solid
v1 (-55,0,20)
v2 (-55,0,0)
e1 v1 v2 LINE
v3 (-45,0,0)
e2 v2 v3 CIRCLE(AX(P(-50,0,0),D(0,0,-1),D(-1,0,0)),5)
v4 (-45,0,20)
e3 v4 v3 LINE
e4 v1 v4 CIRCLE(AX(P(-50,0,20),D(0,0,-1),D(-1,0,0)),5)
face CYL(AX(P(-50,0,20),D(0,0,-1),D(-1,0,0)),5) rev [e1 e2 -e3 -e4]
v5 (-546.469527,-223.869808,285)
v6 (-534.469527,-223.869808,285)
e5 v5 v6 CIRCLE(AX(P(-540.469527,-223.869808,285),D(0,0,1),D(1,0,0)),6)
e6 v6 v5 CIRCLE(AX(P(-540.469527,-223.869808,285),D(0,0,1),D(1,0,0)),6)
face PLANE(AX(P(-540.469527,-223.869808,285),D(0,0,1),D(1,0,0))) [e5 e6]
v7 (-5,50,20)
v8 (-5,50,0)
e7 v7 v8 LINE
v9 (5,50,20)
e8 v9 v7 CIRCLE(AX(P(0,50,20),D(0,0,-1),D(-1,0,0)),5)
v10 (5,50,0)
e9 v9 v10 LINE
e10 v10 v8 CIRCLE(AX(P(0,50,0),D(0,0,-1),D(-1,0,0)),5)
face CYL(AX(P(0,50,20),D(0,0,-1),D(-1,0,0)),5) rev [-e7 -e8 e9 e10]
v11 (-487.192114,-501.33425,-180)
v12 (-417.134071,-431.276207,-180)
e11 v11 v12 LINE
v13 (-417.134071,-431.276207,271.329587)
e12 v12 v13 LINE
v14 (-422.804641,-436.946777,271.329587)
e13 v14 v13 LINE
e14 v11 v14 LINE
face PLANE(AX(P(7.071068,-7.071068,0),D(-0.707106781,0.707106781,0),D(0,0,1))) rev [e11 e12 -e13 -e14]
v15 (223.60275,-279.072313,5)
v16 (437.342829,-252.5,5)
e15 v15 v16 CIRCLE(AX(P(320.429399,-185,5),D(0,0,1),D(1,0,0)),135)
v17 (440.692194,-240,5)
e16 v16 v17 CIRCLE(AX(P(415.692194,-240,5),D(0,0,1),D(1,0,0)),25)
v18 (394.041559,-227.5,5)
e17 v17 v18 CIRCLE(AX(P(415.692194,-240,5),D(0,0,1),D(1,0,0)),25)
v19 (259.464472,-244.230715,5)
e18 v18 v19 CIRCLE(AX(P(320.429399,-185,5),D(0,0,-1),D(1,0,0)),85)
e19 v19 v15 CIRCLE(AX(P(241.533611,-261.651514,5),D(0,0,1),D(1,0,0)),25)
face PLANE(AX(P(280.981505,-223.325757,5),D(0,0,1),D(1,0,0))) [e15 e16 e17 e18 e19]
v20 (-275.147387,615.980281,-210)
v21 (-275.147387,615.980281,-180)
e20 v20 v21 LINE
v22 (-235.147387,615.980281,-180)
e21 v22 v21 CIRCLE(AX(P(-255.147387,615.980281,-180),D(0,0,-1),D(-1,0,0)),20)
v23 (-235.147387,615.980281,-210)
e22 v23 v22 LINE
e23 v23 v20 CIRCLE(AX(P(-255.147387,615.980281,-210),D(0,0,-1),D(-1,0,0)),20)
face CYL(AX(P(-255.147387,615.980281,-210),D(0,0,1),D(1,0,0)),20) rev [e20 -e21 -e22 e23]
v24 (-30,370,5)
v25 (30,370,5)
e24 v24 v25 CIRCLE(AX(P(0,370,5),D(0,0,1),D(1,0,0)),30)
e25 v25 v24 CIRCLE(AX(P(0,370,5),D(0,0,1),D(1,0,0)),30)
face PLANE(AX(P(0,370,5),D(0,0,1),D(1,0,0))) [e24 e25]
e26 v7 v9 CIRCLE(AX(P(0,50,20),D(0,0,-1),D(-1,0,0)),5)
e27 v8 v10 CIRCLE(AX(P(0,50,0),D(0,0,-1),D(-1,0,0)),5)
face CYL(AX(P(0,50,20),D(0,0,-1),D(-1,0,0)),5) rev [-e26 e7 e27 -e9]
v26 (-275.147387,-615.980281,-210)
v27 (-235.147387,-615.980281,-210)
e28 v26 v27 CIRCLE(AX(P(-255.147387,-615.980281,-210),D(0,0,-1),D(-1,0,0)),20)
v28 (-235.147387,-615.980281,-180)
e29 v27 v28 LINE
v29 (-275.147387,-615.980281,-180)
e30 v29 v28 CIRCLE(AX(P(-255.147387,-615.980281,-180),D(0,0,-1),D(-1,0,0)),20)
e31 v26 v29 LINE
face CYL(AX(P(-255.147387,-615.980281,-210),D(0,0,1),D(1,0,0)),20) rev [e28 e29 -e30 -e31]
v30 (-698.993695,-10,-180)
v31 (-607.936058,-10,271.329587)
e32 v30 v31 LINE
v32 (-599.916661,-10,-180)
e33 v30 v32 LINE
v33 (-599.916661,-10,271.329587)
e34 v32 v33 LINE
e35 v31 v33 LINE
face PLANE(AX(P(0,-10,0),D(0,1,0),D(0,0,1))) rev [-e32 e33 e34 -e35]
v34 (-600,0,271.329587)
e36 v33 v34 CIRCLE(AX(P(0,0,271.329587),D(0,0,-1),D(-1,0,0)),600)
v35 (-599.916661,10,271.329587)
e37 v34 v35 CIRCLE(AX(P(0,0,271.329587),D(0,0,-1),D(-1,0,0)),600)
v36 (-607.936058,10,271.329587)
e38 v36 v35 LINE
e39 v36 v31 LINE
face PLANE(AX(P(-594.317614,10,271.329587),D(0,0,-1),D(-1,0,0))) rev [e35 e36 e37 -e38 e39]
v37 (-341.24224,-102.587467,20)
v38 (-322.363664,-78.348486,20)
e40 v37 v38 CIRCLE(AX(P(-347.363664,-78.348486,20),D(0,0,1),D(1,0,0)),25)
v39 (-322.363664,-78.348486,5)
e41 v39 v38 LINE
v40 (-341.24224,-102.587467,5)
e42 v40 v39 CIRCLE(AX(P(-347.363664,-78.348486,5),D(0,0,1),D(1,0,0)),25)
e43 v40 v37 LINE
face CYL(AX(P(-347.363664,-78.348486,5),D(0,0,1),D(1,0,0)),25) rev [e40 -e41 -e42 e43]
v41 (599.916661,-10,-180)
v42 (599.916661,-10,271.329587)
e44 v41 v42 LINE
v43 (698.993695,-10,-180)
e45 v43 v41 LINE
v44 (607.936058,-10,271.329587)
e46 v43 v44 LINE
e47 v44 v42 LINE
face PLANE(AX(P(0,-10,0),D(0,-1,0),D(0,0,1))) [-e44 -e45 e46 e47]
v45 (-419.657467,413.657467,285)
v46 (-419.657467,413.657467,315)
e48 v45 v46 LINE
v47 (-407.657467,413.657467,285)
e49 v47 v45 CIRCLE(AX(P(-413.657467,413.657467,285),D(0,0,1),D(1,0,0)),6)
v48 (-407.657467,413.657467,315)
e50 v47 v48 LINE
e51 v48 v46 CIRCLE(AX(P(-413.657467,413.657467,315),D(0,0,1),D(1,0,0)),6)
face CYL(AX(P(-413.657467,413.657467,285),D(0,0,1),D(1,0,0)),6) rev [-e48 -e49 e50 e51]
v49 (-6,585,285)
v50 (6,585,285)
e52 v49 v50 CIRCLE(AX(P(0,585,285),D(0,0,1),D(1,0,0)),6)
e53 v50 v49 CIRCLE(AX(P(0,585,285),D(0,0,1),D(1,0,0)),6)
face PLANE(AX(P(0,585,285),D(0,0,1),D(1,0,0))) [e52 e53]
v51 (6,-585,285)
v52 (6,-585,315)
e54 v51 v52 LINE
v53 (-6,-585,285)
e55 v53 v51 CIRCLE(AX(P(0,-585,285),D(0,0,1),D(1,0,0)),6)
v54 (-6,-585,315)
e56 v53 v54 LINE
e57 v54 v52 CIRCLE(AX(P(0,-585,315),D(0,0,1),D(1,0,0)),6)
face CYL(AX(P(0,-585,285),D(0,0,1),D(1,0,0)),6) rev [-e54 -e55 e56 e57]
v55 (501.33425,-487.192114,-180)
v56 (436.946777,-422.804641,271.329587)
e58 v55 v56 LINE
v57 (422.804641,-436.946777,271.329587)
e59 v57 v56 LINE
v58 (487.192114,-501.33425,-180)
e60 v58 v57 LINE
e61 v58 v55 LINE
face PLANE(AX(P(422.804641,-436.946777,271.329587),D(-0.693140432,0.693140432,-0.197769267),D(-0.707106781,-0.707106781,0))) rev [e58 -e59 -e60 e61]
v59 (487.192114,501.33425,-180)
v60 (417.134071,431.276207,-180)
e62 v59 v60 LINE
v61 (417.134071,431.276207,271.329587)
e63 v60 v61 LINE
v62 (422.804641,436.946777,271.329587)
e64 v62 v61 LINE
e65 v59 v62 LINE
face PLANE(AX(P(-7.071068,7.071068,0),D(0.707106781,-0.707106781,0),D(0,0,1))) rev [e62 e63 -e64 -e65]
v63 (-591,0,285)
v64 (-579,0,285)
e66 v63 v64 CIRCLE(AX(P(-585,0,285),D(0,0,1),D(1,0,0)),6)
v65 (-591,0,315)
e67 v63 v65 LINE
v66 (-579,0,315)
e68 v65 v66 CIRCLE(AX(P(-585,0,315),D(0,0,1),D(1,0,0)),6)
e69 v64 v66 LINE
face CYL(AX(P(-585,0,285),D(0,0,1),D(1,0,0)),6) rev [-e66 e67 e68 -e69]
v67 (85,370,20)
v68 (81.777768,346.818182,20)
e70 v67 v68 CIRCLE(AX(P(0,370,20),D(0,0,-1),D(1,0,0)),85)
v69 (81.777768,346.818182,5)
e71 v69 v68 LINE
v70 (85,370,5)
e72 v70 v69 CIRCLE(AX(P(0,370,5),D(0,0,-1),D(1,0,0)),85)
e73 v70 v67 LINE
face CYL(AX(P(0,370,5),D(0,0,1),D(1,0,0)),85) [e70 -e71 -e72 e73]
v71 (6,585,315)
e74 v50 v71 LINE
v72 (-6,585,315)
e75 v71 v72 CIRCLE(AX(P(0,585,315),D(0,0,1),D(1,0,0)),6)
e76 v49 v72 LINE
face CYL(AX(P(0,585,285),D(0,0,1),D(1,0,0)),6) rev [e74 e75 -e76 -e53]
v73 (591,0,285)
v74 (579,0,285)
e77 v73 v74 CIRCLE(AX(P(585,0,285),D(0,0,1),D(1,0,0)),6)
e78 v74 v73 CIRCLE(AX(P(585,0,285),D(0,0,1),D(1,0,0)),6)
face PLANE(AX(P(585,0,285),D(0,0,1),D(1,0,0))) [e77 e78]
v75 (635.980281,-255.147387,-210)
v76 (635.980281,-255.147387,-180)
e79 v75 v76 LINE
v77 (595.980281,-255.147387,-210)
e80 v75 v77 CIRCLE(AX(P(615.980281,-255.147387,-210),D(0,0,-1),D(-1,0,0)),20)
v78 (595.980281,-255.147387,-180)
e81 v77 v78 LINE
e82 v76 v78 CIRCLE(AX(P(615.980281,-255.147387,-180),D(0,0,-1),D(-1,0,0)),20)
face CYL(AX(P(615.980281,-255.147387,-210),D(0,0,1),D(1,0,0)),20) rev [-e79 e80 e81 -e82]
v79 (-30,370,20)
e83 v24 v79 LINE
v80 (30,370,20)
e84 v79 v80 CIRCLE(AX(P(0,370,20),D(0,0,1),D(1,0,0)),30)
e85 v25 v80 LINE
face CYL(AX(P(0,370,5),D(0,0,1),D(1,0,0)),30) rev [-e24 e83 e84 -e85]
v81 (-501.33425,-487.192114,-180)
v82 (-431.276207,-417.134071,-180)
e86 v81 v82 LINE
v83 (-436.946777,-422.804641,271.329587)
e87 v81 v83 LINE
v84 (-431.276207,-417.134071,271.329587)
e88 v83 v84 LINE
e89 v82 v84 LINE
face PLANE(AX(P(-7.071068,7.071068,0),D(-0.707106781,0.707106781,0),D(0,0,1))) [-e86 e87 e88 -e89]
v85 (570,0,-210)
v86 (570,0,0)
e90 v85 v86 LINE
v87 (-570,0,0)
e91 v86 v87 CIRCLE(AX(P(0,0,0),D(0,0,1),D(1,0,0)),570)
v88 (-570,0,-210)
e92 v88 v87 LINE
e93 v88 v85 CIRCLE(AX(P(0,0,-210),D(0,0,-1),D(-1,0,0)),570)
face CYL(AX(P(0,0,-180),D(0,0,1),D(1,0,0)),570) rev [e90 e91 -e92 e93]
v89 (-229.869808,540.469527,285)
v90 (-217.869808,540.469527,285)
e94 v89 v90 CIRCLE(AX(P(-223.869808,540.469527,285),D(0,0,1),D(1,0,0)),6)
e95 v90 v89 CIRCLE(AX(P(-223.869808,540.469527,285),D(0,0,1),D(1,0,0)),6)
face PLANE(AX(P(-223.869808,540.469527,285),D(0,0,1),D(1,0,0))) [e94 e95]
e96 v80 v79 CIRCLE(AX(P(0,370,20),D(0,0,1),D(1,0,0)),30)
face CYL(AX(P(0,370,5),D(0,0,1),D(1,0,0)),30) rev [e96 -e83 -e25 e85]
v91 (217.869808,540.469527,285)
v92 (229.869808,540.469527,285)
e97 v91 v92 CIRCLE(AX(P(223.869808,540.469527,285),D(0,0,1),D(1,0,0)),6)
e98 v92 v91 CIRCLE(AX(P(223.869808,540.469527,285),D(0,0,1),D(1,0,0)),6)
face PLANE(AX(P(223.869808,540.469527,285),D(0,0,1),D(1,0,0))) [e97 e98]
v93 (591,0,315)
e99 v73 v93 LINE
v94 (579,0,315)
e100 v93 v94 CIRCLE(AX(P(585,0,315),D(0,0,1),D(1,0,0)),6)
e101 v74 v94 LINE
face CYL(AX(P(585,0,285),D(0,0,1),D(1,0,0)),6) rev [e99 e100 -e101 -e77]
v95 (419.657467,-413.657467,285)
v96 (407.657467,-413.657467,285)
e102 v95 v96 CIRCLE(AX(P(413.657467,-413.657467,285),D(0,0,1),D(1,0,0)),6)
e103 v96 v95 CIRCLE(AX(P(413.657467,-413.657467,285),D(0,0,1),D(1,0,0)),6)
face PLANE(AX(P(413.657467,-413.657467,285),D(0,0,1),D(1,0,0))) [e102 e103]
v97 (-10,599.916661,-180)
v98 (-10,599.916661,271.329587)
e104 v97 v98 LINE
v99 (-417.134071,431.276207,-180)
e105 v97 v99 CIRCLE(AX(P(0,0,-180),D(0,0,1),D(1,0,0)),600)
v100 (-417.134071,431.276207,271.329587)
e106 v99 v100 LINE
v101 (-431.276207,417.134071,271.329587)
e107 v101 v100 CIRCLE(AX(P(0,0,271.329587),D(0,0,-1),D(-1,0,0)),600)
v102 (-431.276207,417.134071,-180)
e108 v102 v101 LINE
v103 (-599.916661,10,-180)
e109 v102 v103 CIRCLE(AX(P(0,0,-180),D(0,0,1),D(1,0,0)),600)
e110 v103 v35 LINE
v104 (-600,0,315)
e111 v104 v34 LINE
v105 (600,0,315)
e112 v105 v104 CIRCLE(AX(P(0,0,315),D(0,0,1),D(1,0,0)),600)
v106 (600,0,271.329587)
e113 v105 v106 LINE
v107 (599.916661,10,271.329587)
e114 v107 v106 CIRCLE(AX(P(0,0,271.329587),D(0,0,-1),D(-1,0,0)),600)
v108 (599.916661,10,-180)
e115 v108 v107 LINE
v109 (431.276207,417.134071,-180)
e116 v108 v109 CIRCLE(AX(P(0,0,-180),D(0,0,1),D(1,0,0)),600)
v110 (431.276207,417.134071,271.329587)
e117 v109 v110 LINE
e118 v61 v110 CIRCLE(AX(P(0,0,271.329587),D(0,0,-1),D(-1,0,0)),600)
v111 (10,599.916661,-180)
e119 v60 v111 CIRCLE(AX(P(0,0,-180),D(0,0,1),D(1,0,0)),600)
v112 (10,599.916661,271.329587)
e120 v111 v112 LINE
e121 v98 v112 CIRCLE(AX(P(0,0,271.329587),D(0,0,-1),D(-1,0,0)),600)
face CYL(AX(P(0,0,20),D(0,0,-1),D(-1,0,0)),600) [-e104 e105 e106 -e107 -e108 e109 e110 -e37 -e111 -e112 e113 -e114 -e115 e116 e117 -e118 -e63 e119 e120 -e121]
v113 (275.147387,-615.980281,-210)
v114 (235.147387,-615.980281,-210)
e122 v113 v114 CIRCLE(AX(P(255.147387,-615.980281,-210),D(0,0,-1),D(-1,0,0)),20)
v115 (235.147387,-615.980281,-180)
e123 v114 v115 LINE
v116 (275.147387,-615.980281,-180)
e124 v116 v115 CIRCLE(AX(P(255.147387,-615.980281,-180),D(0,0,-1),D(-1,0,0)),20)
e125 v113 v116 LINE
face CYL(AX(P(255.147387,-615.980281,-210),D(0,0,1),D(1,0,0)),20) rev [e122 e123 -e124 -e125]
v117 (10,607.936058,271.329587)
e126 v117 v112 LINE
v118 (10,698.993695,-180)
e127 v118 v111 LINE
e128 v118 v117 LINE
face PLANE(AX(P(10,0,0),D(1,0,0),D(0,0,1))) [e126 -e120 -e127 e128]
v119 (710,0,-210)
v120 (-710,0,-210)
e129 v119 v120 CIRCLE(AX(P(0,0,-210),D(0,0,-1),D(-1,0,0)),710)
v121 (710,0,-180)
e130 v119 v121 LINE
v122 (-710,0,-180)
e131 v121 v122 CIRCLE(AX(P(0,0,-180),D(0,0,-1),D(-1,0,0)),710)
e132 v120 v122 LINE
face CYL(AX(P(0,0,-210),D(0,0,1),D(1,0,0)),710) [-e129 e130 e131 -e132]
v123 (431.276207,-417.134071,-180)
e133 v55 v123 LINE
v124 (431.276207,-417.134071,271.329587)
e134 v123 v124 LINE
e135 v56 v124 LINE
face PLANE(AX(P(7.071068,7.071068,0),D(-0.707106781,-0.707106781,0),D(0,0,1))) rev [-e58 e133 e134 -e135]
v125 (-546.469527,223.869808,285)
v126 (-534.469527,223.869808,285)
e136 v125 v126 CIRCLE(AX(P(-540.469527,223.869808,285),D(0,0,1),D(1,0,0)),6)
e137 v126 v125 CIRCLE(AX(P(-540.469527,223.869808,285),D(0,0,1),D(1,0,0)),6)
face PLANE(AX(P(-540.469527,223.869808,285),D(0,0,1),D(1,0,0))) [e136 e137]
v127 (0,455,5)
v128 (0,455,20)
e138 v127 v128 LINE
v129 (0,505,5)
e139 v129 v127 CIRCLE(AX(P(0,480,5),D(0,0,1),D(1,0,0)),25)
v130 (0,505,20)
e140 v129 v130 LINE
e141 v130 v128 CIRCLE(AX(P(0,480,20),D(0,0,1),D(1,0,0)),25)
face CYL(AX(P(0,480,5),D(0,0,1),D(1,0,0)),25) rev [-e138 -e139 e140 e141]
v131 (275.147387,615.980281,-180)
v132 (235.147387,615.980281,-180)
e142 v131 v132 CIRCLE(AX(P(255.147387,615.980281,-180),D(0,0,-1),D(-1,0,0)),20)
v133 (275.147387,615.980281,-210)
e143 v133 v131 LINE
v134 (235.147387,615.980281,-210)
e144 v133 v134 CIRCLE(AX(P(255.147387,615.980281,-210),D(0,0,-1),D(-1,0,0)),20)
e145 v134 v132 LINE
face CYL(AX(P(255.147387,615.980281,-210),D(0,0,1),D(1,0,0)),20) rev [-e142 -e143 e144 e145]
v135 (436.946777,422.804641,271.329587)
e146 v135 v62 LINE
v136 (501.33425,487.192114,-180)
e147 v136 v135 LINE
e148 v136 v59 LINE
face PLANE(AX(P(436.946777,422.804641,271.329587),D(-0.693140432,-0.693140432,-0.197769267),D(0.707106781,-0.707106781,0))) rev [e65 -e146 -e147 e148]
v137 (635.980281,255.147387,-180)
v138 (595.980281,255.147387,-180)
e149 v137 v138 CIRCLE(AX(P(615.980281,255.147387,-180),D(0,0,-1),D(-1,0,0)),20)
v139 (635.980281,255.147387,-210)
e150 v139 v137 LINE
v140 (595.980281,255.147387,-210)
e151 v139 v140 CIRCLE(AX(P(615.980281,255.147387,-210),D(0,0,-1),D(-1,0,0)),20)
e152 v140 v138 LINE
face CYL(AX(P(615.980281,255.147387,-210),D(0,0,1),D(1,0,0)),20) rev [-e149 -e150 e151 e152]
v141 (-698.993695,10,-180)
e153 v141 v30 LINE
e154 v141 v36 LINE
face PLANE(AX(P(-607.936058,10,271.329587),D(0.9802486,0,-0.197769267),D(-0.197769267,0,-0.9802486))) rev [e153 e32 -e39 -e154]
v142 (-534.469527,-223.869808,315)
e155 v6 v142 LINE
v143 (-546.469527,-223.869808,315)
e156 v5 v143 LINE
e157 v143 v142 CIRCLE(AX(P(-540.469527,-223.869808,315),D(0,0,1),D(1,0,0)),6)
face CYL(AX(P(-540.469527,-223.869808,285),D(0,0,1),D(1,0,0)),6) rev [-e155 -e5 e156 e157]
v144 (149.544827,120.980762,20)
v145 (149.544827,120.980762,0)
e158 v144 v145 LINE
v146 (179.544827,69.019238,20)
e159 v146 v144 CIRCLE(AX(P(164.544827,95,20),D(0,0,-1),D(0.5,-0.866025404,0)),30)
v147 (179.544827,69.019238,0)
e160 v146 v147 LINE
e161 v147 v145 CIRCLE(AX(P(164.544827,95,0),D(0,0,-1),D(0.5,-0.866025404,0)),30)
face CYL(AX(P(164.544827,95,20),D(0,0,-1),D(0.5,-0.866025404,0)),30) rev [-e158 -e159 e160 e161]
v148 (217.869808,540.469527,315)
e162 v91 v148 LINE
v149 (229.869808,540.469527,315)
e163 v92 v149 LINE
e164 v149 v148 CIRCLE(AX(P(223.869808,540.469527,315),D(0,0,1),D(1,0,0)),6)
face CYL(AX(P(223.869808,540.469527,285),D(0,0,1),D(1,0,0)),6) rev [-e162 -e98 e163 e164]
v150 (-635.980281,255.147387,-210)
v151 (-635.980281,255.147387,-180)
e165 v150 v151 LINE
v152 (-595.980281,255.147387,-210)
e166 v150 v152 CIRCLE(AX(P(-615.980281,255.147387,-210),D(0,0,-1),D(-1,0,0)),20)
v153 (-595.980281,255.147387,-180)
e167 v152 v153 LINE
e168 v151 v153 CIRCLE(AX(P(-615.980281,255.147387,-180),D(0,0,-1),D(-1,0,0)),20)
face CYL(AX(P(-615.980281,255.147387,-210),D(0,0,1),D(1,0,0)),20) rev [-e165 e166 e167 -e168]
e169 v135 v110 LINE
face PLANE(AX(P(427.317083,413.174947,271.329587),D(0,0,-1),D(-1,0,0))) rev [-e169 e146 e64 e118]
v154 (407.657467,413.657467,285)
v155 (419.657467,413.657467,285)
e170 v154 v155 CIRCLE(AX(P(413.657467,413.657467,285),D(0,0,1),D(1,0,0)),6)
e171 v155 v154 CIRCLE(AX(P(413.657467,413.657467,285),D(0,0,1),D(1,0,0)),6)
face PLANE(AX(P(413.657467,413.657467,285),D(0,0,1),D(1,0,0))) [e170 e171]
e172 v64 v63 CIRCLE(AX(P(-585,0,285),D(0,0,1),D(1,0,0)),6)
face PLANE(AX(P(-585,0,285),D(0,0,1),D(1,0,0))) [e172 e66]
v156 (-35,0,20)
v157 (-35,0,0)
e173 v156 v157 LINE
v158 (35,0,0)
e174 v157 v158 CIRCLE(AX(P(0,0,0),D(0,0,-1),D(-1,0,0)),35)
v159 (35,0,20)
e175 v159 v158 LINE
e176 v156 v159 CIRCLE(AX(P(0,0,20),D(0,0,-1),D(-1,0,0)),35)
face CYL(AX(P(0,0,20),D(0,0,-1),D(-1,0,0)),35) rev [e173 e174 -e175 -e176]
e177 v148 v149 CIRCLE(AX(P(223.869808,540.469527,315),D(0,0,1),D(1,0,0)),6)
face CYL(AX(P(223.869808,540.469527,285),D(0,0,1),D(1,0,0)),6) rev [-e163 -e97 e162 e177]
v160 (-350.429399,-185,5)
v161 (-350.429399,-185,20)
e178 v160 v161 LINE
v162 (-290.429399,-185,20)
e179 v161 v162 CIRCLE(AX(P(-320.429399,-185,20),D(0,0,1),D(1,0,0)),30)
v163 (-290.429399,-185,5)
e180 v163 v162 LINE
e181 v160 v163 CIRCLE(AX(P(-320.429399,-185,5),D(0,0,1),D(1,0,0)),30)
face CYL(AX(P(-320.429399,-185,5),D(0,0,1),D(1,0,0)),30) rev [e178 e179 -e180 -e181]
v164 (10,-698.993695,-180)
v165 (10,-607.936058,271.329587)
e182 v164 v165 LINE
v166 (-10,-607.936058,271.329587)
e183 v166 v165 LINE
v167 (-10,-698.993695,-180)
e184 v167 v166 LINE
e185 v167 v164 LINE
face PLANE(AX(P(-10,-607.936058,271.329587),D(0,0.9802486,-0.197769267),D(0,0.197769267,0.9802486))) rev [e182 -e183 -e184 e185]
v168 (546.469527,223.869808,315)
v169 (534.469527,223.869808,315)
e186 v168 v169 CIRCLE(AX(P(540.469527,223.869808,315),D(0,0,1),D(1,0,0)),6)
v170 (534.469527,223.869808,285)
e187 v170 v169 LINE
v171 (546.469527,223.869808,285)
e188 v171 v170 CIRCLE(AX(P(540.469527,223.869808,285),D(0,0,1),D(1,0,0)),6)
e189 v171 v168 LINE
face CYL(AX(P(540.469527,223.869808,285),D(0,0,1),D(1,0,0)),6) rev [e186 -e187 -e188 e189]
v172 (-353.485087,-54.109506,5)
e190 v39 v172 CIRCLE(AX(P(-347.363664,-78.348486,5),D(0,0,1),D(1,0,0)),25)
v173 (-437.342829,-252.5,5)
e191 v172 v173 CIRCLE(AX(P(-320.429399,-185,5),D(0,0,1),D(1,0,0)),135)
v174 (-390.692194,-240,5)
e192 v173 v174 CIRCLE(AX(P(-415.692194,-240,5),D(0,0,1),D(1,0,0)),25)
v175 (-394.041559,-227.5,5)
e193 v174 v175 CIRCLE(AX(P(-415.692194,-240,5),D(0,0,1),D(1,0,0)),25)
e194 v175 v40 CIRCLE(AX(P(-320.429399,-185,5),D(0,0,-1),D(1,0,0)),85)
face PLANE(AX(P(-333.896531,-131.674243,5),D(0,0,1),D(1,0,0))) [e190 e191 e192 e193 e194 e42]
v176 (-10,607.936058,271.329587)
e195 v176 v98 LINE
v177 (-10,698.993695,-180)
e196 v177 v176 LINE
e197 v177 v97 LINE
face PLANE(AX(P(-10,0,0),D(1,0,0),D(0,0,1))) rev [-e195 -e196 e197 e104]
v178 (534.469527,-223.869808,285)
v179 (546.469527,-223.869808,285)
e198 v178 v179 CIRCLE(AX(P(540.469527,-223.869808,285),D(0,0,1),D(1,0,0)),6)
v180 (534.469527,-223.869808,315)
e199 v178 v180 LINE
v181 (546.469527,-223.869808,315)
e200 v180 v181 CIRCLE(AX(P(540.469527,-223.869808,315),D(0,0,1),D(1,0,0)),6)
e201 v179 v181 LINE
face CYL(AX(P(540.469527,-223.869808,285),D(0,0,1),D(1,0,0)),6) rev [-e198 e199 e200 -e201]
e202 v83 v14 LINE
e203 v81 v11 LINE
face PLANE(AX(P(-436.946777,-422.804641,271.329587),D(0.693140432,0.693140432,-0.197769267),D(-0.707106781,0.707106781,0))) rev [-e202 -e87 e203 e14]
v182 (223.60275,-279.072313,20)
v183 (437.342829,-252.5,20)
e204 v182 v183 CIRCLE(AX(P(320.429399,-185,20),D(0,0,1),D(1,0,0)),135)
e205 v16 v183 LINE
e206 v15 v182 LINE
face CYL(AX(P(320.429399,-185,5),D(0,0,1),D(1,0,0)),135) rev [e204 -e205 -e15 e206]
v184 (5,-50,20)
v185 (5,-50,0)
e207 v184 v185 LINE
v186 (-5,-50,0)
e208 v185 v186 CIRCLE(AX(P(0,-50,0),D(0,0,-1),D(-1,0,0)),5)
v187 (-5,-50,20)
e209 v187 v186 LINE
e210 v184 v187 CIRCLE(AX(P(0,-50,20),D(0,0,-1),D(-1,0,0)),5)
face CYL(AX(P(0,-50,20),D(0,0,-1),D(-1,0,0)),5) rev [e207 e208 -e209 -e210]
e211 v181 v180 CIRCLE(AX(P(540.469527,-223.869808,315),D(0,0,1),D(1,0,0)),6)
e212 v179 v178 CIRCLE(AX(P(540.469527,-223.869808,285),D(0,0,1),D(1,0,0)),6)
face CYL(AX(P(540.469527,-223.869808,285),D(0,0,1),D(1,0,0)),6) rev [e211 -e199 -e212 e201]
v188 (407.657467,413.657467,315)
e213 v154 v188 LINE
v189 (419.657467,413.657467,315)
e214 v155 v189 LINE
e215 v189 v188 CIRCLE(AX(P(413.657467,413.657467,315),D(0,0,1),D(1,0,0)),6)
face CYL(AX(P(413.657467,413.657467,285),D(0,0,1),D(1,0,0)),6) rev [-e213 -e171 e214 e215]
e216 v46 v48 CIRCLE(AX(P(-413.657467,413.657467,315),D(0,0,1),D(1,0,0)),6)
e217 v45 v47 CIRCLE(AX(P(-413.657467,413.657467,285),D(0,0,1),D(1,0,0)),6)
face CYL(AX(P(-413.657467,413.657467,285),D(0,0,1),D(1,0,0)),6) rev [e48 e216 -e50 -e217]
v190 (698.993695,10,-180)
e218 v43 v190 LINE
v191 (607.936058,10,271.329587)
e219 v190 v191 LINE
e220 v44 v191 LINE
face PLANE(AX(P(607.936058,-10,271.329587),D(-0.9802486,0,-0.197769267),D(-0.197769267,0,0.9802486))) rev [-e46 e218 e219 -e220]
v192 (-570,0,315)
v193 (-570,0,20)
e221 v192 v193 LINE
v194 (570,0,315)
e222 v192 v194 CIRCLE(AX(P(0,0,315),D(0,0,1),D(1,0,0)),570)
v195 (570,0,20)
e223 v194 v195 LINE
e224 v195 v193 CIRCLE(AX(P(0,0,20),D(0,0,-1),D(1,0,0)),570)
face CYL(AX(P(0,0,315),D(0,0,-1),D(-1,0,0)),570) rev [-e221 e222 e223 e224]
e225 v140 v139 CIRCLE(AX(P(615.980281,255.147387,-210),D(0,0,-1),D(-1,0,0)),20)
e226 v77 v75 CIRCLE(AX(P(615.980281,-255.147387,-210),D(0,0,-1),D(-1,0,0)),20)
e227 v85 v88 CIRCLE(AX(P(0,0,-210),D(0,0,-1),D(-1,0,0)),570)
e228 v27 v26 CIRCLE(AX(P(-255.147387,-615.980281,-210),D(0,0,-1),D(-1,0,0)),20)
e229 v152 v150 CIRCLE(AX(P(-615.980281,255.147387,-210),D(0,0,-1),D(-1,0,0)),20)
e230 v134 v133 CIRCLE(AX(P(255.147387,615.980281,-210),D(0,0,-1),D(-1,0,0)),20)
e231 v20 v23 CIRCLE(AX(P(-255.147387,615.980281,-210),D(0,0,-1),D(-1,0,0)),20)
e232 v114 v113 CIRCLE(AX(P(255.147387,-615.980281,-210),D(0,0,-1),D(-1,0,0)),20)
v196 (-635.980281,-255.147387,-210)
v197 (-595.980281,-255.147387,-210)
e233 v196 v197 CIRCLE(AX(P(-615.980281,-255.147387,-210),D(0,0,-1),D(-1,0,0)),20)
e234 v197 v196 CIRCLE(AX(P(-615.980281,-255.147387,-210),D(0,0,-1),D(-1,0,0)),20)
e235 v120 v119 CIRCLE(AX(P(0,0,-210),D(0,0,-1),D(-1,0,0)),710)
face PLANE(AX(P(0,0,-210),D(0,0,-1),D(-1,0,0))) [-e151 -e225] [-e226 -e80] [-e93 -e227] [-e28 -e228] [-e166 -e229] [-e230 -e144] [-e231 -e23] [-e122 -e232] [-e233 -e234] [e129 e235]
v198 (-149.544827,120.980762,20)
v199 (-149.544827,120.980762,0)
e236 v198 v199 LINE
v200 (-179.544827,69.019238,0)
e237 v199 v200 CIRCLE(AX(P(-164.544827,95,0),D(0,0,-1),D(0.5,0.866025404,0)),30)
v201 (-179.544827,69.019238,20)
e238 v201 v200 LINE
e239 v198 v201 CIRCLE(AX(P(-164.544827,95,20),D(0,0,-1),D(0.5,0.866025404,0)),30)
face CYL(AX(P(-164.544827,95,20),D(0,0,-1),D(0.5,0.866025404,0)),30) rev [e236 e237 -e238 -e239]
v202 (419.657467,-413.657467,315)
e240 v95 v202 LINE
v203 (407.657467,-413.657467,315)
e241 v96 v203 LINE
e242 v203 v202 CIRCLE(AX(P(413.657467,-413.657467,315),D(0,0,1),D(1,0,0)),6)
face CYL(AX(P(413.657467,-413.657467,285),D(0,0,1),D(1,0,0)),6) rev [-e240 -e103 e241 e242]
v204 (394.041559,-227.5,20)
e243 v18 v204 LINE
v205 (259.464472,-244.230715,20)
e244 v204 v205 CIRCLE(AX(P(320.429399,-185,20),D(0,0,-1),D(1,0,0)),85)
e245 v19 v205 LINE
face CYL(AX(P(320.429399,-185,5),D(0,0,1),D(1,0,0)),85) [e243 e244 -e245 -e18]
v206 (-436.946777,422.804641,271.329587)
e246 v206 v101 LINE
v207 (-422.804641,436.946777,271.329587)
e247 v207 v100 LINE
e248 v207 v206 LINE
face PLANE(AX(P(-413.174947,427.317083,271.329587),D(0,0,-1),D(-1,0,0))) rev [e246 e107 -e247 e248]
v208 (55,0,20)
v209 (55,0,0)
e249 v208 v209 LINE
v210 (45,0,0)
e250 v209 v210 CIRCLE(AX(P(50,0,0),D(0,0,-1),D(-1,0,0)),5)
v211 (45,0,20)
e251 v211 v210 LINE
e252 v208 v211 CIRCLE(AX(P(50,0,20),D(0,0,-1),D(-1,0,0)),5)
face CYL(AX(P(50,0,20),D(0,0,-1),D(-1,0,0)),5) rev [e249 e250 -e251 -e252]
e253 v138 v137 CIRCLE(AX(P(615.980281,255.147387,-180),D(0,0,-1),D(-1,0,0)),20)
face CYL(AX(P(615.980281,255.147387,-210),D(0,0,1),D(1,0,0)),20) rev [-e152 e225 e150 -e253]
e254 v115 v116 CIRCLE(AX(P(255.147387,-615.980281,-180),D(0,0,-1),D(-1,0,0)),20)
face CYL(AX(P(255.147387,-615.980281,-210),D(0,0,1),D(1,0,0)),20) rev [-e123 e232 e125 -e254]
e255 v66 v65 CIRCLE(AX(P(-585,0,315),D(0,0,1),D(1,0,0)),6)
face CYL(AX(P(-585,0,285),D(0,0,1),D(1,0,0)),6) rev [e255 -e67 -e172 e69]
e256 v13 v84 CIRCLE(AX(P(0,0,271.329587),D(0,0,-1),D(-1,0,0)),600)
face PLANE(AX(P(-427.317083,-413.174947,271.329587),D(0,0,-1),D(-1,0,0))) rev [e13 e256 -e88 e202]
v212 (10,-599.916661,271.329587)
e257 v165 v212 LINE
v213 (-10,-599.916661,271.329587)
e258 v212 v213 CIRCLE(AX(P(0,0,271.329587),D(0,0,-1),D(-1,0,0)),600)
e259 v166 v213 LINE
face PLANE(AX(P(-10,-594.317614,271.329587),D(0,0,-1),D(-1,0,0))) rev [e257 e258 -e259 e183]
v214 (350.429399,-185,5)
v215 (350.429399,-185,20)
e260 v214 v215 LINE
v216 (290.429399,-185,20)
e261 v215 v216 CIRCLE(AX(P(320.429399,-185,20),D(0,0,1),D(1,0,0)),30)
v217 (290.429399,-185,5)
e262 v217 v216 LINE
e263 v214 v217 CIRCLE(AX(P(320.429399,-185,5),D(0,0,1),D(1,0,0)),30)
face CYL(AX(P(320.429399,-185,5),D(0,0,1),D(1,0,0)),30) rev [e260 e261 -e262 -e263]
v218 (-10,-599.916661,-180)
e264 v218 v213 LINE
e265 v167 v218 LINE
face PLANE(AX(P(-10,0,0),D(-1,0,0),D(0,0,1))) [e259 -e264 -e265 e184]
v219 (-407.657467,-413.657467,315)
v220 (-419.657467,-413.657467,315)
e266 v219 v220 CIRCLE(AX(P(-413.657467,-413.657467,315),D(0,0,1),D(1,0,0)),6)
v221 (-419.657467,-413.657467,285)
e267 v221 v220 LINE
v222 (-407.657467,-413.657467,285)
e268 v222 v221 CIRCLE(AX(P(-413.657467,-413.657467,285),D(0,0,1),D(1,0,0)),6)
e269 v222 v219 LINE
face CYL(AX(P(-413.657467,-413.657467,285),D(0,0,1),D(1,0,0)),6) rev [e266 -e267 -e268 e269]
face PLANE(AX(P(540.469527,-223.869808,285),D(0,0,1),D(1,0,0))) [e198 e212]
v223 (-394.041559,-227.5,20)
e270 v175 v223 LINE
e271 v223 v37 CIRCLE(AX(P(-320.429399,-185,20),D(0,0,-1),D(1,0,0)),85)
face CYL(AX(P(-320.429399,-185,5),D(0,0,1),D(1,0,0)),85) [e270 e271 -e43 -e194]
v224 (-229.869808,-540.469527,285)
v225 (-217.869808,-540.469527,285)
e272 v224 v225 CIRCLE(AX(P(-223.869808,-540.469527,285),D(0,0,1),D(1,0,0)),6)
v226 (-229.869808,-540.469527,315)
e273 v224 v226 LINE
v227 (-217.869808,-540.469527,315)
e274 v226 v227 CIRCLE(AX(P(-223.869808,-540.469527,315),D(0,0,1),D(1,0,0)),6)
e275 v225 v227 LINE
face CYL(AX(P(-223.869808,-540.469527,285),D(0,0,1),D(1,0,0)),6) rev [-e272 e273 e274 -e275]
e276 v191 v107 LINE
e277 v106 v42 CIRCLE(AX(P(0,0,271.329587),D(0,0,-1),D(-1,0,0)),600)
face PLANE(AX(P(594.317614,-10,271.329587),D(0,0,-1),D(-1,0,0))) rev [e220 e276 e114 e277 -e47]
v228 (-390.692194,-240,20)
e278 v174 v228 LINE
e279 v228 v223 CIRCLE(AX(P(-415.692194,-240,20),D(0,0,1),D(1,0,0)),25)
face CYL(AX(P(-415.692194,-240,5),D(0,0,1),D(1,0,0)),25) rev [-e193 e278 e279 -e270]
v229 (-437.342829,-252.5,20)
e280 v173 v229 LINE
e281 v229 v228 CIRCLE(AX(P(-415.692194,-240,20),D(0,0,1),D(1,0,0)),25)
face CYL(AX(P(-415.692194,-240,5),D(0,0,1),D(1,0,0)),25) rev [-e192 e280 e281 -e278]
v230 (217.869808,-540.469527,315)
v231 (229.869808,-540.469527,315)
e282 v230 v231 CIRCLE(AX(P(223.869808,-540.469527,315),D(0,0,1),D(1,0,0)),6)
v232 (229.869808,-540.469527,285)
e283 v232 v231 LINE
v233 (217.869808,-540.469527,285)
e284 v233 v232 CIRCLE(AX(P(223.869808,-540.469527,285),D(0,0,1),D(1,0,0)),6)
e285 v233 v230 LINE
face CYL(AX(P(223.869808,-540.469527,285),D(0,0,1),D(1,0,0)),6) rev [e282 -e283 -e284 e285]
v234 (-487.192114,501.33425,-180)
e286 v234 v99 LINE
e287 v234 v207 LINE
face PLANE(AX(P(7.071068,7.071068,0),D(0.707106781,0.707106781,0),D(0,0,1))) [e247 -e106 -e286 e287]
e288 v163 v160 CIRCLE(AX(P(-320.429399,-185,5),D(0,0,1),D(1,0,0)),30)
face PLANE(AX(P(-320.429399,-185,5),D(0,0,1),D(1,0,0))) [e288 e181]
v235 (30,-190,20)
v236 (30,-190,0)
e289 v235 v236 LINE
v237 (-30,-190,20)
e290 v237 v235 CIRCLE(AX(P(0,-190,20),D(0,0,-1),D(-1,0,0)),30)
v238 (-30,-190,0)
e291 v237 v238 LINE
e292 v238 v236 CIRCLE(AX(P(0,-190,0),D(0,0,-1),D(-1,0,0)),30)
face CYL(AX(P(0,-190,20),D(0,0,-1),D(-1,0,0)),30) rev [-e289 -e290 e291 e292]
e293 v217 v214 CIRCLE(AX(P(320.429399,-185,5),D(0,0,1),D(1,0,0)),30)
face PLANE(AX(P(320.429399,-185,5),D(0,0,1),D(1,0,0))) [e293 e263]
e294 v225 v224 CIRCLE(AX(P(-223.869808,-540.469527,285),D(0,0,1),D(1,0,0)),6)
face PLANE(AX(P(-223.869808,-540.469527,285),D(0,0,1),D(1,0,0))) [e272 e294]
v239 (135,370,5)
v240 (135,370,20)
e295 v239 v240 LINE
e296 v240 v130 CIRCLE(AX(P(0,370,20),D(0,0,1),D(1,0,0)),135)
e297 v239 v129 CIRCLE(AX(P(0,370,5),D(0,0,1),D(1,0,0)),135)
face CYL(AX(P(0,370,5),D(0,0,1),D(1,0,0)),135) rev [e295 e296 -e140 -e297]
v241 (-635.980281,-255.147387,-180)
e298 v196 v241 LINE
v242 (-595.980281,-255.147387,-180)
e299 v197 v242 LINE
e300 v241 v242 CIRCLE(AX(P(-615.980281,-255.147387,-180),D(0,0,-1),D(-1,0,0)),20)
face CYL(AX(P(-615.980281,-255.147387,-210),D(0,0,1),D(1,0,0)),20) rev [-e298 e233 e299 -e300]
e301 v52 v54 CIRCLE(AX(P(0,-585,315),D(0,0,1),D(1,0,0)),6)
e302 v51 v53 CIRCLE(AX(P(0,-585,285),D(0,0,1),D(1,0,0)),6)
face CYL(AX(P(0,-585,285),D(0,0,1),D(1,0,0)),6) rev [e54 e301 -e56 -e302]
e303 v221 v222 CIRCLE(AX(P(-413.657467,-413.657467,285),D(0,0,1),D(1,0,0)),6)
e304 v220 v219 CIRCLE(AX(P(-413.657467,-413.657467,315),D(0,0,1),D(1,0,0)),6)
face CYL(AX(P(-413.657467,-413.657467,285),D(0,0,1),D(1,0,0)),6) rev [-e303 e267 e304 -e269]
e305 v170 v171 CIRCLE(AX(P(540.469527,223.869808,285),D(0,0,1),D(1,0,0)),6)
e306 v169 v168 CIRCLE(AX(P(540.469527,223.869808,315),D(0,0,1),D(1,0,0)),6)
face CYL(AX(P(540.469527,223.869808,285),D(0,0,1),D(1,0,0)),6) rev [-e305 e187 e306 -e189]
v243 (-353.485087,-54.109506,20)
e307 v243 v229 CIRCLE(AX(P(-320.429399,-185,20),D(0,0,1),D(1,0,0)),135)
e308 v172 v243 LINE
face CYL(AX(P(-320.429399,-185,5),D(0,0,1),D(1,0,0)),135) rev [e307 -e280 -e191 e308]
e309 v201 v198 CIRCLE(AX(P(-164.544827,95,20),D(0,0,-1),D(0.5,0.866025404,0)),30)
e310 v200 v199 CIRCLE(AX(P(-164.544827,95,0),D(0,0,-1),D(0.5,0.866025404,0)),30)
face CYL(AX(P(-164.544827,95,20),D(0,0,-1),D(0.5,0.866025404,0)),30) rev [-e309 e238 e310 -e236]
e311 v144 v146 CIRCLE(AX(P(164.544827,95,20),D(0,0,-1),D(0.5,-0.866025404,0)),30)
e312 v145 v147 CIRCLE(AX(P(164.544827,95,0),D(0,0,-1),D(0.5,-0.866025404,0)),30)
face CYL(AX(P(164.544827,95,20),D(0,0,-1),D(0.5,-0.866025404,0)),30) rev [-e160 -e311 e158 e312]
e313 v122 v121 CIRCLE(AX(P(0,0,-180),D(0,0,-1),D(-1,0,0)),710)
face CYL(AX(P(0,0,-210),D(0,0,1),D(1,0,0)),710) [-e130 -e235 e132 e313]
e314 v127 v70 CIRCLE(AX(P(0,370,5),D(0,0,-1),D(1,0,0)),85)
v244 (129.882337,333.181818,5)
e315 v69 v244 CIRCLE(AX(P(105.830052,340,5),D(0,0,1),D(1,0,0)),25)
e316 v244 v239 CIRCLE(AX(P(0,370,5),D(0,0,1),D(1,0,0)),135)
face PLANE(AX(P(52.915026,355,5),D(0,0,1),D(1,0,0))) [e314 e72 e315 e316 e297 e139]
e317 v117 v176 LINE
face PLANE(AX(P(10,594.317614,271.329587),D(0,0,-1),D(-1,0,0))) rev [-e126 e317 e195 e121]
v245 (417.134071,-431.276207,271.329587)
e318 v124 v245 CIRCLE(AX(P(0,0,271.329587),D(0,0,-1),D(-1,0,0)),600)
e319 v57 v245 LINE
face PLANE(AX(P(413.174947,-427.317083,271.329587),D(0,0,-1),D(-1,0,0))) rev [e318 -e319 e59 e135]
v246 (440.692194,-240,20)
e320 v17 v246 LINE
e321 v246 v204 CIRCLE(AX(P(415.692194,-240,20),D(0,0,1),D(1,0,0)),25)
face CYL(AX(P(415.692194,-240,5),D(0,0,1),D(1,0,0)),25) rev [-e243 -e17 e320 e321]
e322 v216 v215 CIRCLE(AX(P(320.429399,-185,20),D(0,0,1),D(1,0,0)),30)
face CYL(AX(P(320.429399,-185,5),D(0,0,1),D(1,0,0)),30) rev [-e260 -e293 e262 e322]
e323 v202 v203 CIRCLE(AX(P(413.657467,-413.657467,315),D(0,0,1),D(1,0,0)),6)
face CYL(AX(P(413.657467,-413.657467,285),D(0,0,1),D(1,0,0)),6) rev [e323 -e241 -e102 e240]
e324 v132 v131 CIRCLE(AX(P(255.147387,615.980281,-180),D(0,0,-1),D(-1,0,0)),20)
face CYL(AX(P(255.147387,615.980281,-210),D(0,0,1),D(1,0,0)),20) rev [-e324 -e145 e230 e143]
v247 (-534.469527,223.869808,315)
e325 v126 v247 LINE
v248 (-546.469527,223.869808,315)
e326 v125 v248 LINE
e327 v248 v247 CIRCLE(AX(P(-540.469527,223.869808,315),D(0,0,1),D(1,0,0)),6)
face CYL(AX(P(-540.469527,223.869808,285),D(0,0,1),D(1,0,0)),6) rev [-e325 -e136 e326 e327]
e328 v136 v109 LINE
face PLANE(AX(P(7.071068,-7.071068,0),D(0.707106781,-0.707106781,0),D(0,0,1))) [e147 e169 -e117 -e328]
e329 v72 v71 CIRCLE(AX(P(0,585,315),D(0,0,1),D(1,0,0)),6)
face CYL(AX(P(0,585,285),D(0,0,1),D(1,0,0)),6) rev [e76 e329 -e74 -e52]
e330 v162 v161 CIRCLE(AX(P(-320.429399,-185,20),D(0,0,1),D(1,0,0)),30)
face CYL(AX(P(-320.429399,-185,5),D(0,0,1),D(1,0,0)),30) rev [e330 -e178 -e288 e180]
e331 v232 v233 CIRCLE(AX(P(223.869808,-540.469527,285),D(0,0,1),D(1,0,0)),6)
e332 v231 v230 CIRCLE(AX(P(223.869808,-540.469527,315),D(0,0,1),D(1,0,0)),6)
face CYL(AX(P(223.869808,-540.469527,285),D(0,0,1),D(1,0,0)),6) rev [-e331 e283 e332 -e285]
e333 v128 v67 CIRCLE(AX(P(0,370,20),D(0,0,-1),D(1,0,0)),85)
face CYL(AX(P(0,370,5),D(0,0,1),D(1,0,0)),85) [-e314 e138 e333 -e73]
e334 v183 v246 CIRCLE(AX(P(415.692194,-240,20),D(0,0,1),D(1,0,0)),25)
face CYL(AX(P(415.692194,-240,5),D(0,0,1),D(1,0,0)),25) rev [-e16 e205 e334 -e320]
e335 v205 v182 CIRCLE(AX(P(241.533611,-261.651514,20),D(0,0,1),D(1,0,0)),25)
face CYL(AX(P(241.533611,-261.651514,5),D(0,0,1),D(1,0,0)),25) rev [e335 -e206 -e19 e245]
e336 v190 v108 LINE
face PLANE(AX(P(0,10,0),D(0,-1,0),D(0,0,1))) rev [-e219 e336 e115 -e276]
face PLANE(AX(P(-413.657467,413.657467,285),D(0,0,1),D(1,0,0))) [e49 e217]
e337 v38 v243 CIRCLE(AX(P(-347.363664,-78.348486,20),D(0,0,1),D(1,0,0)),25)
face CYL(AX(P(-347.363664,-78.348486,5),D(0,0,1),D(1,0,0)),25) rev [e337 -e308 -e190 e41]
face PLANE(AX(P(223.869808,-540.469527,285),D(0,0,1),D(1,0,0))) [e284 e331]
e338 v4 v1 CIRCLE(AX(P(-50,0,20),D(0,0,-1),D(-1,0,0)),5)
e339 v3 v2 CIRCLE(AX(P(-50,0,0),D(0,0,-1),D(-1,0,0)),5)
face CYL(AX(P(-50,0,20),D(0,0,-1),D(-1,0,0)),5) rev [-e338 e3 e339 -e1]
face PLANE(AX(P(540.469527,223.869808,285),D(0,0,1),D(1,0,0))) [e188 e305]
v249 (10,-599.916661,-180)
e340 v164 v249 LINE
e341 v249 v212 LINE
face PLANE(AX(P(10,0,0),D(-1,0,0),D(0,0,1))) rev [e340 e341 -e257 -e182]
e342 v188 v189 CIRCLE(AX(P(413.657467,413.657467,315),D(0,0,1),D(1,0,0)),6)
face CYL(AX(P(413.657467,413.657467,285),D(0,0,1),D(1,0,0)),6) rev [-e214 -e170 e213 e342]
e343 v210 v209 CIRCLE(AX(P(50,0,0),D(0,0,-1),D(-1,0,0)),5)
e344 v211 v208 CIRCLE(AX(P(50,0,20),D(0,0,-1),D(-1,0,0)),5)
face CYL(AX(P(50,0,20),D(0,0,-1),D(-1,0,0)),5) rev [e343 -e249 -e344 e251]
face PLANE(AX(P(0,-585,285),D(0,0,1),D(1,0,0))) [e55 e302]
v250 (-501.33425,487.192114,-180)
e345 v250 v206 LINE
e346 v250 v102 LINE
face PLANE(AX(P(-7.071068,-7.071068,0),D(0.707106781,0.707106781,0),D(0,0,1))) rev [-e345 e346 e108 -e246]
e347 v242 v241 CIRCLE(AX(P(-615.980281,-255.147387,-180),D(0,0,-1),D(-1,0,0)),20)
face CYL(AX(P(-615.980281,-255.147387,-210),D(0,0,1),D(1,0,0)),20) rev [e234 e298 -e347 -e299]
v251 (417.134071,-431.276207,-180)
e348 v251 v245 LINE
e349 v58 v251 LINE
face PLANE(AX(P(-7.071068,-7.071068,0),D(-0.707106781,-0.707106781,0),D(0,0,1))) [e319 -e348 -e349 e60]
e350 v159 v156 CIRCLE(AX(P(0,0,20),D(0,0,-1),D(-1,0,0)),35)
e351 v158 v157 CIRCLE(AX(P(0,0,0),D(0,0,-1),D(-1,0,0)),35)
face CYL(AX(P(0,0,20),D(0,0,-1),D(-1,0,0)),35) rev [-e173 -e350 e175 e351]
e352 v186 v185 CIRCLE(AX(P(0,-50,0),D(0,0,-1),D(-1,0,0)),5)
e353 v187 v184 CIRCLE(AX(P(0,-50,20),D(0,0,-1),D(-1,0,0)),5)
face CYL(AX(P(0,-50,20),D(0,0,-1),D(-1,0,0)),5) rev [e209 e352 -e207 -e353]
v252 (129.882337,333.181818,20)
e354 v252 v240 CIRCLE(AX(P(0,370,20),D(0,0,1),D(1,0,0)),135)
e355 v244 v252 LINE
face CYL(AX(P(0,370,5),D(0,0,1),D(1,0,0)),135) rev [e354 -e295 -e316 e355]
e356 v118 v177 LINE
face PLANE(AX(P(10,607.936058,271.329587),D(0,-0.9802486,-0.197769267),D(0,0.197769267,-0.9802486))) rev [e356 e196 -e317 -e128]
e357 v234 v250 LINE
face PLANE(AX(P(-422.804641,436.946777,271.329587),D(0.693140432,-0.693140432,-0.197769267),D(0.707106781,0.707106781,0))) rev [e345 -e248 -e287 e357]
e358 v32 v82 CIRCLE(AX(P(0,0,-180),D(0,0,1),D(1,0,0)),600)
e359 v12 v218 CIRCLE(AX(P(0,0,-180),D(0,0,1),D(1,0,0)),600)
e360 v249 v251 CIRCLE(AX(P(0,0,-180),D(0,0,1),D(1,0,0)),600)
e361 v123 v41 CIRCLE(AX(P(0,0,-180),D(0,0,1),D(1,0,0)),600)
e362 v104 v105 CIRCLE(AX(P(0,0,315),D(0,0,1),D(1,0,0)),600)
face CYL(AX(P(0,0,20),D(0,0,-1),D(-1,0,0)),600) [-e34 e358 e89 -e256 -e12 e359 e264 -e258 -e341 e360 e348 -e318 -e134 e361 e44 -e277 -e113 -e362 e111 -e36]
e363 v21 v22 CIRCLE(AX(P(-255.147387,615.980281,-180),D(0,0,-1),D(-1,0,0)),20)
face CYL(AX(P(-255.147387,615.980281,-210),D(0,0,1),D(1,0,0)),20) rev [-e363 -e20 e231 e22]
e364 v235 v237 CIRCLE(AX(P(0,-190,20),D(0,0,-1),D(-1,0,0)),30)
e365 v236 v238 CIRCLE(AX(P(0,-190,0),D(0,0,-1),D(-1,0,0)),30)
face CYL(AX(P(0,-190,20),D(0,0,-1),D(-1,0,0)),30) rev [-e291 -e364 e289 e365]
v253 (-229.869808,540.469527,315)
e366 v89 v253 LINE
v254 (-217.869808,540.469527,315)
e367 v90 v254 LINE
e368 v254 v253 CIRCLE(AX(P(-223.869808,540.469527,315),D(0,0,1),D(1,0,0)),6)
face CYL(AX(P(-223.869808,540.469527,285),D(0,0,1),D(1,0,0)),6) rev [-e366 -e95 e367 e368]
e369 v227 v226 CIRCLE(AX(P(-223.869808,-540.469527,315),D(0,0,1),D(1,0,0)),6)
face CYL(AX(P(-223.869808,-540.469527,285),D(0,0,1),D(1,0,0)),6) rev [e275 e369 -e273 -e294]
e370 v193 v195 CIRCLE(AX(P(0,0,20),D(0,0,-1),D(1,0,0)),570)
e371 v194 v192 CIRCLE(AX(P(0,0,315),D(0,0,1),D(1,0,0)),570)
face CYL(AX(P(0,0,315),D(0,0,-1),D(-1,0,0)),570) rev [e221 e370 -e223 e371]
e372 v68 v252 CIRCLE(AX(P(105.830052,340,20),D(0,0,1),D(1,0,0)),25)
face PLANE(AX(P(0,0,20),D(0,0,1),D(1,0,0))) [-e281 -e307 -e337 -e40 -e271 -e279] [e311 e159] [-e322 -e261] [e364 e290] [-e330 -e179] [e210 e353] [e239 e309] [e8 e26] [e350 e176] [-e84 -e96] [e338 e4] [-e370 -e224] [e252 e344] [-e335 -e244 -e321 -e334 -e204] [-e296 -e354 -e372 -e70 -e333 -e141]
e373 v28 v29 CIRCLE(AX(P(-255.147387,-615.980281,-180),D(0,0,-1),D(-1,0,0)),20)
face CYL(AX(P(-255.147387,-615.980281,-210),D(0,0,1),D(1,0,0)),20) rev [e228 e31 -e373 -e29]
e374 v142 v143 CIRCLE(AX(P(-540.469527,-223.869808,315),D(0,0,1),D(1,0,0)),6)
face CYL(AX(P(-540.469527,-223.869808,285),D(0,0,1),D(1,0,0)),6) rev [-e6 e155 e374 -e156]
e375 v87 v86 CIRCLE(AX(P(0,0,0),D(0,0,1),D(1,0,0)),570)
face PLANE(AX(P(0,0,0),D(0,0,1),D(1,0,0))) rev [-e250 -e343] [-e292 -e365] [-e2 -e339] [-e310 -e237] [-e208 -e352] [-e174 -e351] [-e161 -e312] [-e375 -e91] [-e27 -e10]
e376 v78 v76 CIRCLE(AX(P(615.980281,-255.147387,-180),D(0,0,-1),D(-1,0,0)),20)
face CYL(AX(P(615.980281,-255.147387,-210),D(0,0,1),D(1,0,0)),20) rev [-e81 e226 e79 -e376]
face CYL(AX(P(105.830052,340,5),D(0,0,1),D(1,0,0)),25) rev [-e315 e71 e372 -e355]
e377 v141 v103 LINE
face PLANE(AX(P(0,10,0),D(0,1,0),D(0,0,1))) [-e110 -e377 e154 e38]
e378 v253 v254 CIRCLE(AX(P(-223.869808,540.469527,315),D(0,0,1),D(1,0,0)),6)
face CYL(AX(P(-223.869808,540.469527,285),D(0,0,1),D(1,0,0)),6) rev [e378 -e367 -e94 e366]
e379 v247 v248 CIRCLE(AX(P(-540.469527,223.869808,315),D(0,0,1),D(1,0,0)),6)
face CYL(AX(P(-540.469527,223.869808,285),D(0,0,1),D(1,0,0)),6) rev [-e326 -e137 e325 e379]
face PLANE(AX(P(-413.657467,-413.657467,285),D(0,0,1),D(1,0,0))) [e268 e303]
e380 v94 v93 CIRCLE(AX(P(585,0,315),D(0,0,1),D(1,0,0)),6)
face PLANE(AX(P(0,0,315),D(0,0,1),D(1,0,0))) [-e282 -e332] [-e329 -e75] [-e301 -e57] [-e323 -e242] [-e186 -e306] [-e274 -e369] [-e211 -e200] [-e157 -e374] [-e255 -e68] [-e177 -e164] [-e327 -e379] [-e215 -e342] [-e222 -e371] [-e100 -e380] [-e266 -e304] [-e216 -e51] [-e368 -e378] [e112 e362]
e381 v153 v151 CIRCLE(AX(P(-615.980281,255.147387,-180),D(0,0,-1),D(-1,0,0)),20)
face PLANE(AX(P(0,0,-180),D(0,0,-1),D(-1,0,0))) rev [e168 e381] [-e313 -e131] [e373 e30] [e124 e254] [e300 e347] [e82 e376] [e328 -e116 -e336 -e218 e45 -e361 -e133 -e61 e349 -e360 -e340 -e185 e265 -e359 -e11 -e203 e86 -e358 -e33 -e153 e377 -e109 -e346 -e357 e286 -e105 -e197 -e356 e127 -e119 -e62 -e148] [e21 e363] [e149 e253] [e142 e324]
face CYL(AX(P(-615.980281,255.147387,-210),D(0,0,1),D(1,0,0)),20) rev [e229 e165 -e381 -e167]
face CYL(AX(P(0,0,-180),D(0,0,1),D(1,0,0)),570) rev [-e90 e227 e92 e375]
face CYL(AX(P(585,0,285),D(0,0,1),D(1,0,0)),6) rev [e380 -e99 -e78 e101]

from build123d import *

# Parameters (mm, degrees)
SKETCH1_R           = 600
BOSS_EXTRUDE1_DEPTH = 20
SKETCH2_R           = 35
SKETCH2_R_2         = 5
CUT_EXTRUDE1_DEPTH  = 849.763806957
SKETCH3_R           = 30
CUT_EXTRUDE2_DEPTH  = 849.763806957
CIRPATTERN1_COUNT   = 3
BOSS_EXTRUDE2_START = -200
SKETCH4_R           = 600
SKETCH4_R_2         = 570
BOSS_EXTRUDE2_DEPTH = 200
SKETCH6_R           = 30
CUT_EXTRUDE3_DEPTH  = 15
SKETCH7_R           = 600
SKETCH7_R_2         = 570
BOSS_EXTRUDE3_DEPTH = 295
BOSS_EXTRUDE4_START = 30
SKETCH8_R           = 710
SKETCH8_R_2         = 570
SKETCH8_R_3         = 20
BOSS_EXTRUDE4_DEPTH = 30
SKETCH9_R           = 6
CUT_EXTRUDE4_DEPTH  = 30
BOSS_EXTRUDE5_DEPTH = 10
CIRPATTERN2_COUNT   = 8


with BuildPart() as part:
    # Sketch1 → Boss-Extrude1 (new body)
    with BuildSketch(Plane.XY):
        Circle(SKETCH1_R)
    extrude(amount=BOSS_EXTRUDE1_DEPTH)

    # Sketch2 → Cut-Extrude1 (cut, through all)
    with BuildSketch(Plane(origin=(0, 0, 0), x_dir=(-1, 0, 0), z_dir=(0, 0, -1))):
        Circle(SKETCH2_R)
        with Locations((50, 0)):
            Circle(SKETCH2_R_2)
        with Locations((0, -50)):
            Circle(SKETCH2_R_2)
        with Locations((-50, 0)):
            Circle(SKETCH2_R_2)
        with Locations((0, 50)):
            Circle(SKETCH2_R_2)
    extrude(amount=-CUT_EXTRUDE1_DEPTH, mode=Mode.SUBTRACT)

    # Sketch3 → Cut-Extrude2 (cut, through all)
    with BuildSketch(Plane(origin=(0, 0, 0), x_dir=(-1, 0, 0), z_dir=(0, 0, -1))):
        with Locations((0, -190)):
            Circle(SKETCH3_R)
    cut_extrude2 = extrude(amount=-CUT_EXTRUDE2_DEPTH, mode=Mode.SUBTRACT)

    # CirPattern1: Cut-Extrude2 ×3 about axis
    cirpattern1_axis = Axis((0, 0, 0), (0, 0, 1))
    for i in range(1, CIRPATTERN1_COUNT):
        add(cut_extrude2.rotate(cirpattern1_axis, i * 360 / CIRPATTERN1_COUNT), mode=Mode.SUBTRACT)

    # Sketch4 → Boss-Extrude2 (add)
    with BuildSketch(Plane.XY.offset(20).offset(BOSS_EXTRUDE2_START)):
        Circle(SKETCH4_R)
        Circle(SKETCH4_R_2, mode=Mode.SUBTRACT)
    extrude(amount=BOSS_EXTRUDE2_DEPTH)

    # Sketch6 → Cut-Extrude3 (cut)
    with BuildSketch(Plane.XY.offset(20)):
        with Locations((0, 370)):
            Circle(SKETCH6_R)
        with Locations((320.4293994, -185)):
            Circle(SKETCH6_R)
        with Locations((-320.4293994, -185)):
            Circle(SKETCH6_R)
        with BuildLine():
            ThreePointArc((437.342828911, -252.5), (428.192193817, -218.349364905), (394.041558722, -227.5))
            ThreePointArc((394.041558722, -227.5), (330.915930172, -269.350653064), (259.464472051, -244.230715286))
            ThreePointArc((259.464472051, -244.230715286), (224.112812452, -243.720652914), (223.60275008, -279.072312513))
            ThreePointArc((223.60275008, -279.072312513), (337.084477685, -318.968684279), (437.342828911, -252.5))
        make_face()
        with BuildLine():
            ThreePointArc((-437.342828911, -252.5), (-403.192193817, -261.650635095), (-394.041558722, -227.5))
            ThreePointArc((-394.041558722, -227.5), (-398.722473166, -151.906275514), (-341.242239847, -102.587466532))
            ThreePointArc((-341.242239847, -102.587466532), (-323.124683076, -72.22706244), (-353.485087169, -54.109505669))
            ThreePointArc((-353.485087169, -54.109505669), (-444.777222439, -132.439378757), (-437.342828911, -252.5))
        make_face()
        with BuildLine():
            ThreePointArc((81.777767797, 346.818181818), (67.806542993, 421.256928578), (0, 455))
            ThreePointArc((0, 455), (-25, 480), (0, 505))
            ThreePointArc((0, 505), (107.692744754, 451.408063036), (129.882337089, 333.181818182))
            ThreePointArc((129.882337089, 333.181818182), (99.011870624, 315.947715354), (81.777767797, 346.818181818))
        make_face()
    extrude(amount=-CUT_EXTRUDE3_DEPTH, mode=Mode.SUBTRACT)

    # Sketch7 → Boss-Extrude3 (add)
    with BuildSketch(Plane.XY.offset(20)):
        Circle(SKETCH7_R)
        Circle(SKETCH7_R_2, mode=Mode.SUBTRACT)
    extrude(amount=BOSS_EXTRUDE3_DEPTH)

    # Sketch8 → Boss-Extrude4 (add)
    with BuildSketch(Plane(origin=(0, 0, -180), x_dir=(-1, 0, 0), z_dir=(0, 0, -1)).offset(BOSS_EXTRUDE4_START)):
        Circle(SKETCH8_R)
        with Locations(Location((0, 0, 0), (0, 0, 180))):
            Circle(SKETCH8_R_2, mode=Mode.SUBTRACT)
        with Locations((-615.980281024, 255.147386555)):
            Circle(SKETCH8_R_3, mode=Mode.SUBTRACT)
        with Locations((-255.147386555, 615.980281024)):
            Circle(SKETCH8_R_3, mode=Mode.SUBTRACT)
        with Locations((255.147386555, 615.980281024)):
            Circle(SKETCH8_R_3, mode=Mode.SUBTRACT)
        with Locations((615.980281024, 255.147386555)):
            Circle(SKETCH8_R_3, mode=Mode.SUBTRACT)
        with Locations((615.980281024, -255.147386555)):
            Circle(SKETCH8_R_3, mode=Mode.SUBTRACT)
        with Locations((255.147386555, -615.980281024)):
            Circle(SKETCH8_R_3, mode=Mode.SUBTRACT)
        with Locations((-255.147386555, -615.980281024)):
            Circle(SKETCH8_R_3, mode=Mode.SUBTRACT)
        with Locations((-615.980281024, -255.147386555)):
            Circle(SKETCH8_R_3, mode=Mode.SUBTRACT)
    extrude(amount=-BOSS_EXTRUDE4_DEPTH)

    # Sketch9 → Cut-Extrude4 (cut)
    with BuildSketch(Plane.XY.offset(315)):
        with Locations((585, 0)):
            Circle(SKETCH9_R)
        with Locations((540.469526519, -223.869807934)):
            Circle(SKETCH9_R)
        with Locations((413.657466994, -413.657466994)):
            Circle(SKETCH9_R)
        with Locations((223.869807934, -540.469526519)):
            Circle(SKETCH9_R)
        with Locations((0, -585)):
            Circle(SKETCH9_R)
        with Locations((-223.869807934, -540.469526519)):
            Circle(SKETCH9_R)
        with Locations((-413.657466994, -413.657466994)):
            Circle(SKETCH9_R)
        with Locations((-540.469526519, -223.869807934)):
            Circle(SKETCH9_R)
        with Locations((-585, 0)):
            Circle(SKETCH9_R)
        with Locations((-540.469526519, 223.869807934)):
            Circle(SKETCH9_R)
        with Locations((-413.657466994, 413.657466994)):
            Circle(SKETCH9_R)
        with Locations((-223.869807934, 540.469526519)):
            Circle(SKETCH9_R)
        with Locations((0, 585)):
            Circle(SKETCH9_R)
        with Locations((223.869807934, 540.469526519)):
            Circle(SKETCH9_R)
        with Locations((413.657466994, 413.657466994)):
            Circle(SKETCH9_R)
        with Locations((540.469526519, 223.869807934)):
            Circle(SKETCH9_R)
    extrude(amount=-CUT_EXTRUDE4_DEPTH, mode=Mode.SUBTRACT)

    # Sketch10 → Boss-Extrude5 (add, symmetric)
    with BuildSketch(Plane(origin=(0, 0, 0), x_dir=(1, 0, 0), z_dir=(0, 1, 0))):
        Polygon((-594.317613538, 180), (-594.317613538, -271.329587104), (-607.936057575, -271.329587104), (-698.993694982, 180), align=None)
    boss_extrude5 = extrude(amount=BOSS_EXTRUDE5_DEPTH, both=True)

    # CirPattern2: Boss-Extrude5 ×8 about axis
    cirpattern2_axis = Axis((0, 0, 0), (0, 0, 1))
    for i in range(1, CIRPATTERN2_COUNT):
        add(boss_extrude5.rotate(cirpattern2_axis, i * 360 / CIRPATTERN2_COUNT))


solid = part.part
